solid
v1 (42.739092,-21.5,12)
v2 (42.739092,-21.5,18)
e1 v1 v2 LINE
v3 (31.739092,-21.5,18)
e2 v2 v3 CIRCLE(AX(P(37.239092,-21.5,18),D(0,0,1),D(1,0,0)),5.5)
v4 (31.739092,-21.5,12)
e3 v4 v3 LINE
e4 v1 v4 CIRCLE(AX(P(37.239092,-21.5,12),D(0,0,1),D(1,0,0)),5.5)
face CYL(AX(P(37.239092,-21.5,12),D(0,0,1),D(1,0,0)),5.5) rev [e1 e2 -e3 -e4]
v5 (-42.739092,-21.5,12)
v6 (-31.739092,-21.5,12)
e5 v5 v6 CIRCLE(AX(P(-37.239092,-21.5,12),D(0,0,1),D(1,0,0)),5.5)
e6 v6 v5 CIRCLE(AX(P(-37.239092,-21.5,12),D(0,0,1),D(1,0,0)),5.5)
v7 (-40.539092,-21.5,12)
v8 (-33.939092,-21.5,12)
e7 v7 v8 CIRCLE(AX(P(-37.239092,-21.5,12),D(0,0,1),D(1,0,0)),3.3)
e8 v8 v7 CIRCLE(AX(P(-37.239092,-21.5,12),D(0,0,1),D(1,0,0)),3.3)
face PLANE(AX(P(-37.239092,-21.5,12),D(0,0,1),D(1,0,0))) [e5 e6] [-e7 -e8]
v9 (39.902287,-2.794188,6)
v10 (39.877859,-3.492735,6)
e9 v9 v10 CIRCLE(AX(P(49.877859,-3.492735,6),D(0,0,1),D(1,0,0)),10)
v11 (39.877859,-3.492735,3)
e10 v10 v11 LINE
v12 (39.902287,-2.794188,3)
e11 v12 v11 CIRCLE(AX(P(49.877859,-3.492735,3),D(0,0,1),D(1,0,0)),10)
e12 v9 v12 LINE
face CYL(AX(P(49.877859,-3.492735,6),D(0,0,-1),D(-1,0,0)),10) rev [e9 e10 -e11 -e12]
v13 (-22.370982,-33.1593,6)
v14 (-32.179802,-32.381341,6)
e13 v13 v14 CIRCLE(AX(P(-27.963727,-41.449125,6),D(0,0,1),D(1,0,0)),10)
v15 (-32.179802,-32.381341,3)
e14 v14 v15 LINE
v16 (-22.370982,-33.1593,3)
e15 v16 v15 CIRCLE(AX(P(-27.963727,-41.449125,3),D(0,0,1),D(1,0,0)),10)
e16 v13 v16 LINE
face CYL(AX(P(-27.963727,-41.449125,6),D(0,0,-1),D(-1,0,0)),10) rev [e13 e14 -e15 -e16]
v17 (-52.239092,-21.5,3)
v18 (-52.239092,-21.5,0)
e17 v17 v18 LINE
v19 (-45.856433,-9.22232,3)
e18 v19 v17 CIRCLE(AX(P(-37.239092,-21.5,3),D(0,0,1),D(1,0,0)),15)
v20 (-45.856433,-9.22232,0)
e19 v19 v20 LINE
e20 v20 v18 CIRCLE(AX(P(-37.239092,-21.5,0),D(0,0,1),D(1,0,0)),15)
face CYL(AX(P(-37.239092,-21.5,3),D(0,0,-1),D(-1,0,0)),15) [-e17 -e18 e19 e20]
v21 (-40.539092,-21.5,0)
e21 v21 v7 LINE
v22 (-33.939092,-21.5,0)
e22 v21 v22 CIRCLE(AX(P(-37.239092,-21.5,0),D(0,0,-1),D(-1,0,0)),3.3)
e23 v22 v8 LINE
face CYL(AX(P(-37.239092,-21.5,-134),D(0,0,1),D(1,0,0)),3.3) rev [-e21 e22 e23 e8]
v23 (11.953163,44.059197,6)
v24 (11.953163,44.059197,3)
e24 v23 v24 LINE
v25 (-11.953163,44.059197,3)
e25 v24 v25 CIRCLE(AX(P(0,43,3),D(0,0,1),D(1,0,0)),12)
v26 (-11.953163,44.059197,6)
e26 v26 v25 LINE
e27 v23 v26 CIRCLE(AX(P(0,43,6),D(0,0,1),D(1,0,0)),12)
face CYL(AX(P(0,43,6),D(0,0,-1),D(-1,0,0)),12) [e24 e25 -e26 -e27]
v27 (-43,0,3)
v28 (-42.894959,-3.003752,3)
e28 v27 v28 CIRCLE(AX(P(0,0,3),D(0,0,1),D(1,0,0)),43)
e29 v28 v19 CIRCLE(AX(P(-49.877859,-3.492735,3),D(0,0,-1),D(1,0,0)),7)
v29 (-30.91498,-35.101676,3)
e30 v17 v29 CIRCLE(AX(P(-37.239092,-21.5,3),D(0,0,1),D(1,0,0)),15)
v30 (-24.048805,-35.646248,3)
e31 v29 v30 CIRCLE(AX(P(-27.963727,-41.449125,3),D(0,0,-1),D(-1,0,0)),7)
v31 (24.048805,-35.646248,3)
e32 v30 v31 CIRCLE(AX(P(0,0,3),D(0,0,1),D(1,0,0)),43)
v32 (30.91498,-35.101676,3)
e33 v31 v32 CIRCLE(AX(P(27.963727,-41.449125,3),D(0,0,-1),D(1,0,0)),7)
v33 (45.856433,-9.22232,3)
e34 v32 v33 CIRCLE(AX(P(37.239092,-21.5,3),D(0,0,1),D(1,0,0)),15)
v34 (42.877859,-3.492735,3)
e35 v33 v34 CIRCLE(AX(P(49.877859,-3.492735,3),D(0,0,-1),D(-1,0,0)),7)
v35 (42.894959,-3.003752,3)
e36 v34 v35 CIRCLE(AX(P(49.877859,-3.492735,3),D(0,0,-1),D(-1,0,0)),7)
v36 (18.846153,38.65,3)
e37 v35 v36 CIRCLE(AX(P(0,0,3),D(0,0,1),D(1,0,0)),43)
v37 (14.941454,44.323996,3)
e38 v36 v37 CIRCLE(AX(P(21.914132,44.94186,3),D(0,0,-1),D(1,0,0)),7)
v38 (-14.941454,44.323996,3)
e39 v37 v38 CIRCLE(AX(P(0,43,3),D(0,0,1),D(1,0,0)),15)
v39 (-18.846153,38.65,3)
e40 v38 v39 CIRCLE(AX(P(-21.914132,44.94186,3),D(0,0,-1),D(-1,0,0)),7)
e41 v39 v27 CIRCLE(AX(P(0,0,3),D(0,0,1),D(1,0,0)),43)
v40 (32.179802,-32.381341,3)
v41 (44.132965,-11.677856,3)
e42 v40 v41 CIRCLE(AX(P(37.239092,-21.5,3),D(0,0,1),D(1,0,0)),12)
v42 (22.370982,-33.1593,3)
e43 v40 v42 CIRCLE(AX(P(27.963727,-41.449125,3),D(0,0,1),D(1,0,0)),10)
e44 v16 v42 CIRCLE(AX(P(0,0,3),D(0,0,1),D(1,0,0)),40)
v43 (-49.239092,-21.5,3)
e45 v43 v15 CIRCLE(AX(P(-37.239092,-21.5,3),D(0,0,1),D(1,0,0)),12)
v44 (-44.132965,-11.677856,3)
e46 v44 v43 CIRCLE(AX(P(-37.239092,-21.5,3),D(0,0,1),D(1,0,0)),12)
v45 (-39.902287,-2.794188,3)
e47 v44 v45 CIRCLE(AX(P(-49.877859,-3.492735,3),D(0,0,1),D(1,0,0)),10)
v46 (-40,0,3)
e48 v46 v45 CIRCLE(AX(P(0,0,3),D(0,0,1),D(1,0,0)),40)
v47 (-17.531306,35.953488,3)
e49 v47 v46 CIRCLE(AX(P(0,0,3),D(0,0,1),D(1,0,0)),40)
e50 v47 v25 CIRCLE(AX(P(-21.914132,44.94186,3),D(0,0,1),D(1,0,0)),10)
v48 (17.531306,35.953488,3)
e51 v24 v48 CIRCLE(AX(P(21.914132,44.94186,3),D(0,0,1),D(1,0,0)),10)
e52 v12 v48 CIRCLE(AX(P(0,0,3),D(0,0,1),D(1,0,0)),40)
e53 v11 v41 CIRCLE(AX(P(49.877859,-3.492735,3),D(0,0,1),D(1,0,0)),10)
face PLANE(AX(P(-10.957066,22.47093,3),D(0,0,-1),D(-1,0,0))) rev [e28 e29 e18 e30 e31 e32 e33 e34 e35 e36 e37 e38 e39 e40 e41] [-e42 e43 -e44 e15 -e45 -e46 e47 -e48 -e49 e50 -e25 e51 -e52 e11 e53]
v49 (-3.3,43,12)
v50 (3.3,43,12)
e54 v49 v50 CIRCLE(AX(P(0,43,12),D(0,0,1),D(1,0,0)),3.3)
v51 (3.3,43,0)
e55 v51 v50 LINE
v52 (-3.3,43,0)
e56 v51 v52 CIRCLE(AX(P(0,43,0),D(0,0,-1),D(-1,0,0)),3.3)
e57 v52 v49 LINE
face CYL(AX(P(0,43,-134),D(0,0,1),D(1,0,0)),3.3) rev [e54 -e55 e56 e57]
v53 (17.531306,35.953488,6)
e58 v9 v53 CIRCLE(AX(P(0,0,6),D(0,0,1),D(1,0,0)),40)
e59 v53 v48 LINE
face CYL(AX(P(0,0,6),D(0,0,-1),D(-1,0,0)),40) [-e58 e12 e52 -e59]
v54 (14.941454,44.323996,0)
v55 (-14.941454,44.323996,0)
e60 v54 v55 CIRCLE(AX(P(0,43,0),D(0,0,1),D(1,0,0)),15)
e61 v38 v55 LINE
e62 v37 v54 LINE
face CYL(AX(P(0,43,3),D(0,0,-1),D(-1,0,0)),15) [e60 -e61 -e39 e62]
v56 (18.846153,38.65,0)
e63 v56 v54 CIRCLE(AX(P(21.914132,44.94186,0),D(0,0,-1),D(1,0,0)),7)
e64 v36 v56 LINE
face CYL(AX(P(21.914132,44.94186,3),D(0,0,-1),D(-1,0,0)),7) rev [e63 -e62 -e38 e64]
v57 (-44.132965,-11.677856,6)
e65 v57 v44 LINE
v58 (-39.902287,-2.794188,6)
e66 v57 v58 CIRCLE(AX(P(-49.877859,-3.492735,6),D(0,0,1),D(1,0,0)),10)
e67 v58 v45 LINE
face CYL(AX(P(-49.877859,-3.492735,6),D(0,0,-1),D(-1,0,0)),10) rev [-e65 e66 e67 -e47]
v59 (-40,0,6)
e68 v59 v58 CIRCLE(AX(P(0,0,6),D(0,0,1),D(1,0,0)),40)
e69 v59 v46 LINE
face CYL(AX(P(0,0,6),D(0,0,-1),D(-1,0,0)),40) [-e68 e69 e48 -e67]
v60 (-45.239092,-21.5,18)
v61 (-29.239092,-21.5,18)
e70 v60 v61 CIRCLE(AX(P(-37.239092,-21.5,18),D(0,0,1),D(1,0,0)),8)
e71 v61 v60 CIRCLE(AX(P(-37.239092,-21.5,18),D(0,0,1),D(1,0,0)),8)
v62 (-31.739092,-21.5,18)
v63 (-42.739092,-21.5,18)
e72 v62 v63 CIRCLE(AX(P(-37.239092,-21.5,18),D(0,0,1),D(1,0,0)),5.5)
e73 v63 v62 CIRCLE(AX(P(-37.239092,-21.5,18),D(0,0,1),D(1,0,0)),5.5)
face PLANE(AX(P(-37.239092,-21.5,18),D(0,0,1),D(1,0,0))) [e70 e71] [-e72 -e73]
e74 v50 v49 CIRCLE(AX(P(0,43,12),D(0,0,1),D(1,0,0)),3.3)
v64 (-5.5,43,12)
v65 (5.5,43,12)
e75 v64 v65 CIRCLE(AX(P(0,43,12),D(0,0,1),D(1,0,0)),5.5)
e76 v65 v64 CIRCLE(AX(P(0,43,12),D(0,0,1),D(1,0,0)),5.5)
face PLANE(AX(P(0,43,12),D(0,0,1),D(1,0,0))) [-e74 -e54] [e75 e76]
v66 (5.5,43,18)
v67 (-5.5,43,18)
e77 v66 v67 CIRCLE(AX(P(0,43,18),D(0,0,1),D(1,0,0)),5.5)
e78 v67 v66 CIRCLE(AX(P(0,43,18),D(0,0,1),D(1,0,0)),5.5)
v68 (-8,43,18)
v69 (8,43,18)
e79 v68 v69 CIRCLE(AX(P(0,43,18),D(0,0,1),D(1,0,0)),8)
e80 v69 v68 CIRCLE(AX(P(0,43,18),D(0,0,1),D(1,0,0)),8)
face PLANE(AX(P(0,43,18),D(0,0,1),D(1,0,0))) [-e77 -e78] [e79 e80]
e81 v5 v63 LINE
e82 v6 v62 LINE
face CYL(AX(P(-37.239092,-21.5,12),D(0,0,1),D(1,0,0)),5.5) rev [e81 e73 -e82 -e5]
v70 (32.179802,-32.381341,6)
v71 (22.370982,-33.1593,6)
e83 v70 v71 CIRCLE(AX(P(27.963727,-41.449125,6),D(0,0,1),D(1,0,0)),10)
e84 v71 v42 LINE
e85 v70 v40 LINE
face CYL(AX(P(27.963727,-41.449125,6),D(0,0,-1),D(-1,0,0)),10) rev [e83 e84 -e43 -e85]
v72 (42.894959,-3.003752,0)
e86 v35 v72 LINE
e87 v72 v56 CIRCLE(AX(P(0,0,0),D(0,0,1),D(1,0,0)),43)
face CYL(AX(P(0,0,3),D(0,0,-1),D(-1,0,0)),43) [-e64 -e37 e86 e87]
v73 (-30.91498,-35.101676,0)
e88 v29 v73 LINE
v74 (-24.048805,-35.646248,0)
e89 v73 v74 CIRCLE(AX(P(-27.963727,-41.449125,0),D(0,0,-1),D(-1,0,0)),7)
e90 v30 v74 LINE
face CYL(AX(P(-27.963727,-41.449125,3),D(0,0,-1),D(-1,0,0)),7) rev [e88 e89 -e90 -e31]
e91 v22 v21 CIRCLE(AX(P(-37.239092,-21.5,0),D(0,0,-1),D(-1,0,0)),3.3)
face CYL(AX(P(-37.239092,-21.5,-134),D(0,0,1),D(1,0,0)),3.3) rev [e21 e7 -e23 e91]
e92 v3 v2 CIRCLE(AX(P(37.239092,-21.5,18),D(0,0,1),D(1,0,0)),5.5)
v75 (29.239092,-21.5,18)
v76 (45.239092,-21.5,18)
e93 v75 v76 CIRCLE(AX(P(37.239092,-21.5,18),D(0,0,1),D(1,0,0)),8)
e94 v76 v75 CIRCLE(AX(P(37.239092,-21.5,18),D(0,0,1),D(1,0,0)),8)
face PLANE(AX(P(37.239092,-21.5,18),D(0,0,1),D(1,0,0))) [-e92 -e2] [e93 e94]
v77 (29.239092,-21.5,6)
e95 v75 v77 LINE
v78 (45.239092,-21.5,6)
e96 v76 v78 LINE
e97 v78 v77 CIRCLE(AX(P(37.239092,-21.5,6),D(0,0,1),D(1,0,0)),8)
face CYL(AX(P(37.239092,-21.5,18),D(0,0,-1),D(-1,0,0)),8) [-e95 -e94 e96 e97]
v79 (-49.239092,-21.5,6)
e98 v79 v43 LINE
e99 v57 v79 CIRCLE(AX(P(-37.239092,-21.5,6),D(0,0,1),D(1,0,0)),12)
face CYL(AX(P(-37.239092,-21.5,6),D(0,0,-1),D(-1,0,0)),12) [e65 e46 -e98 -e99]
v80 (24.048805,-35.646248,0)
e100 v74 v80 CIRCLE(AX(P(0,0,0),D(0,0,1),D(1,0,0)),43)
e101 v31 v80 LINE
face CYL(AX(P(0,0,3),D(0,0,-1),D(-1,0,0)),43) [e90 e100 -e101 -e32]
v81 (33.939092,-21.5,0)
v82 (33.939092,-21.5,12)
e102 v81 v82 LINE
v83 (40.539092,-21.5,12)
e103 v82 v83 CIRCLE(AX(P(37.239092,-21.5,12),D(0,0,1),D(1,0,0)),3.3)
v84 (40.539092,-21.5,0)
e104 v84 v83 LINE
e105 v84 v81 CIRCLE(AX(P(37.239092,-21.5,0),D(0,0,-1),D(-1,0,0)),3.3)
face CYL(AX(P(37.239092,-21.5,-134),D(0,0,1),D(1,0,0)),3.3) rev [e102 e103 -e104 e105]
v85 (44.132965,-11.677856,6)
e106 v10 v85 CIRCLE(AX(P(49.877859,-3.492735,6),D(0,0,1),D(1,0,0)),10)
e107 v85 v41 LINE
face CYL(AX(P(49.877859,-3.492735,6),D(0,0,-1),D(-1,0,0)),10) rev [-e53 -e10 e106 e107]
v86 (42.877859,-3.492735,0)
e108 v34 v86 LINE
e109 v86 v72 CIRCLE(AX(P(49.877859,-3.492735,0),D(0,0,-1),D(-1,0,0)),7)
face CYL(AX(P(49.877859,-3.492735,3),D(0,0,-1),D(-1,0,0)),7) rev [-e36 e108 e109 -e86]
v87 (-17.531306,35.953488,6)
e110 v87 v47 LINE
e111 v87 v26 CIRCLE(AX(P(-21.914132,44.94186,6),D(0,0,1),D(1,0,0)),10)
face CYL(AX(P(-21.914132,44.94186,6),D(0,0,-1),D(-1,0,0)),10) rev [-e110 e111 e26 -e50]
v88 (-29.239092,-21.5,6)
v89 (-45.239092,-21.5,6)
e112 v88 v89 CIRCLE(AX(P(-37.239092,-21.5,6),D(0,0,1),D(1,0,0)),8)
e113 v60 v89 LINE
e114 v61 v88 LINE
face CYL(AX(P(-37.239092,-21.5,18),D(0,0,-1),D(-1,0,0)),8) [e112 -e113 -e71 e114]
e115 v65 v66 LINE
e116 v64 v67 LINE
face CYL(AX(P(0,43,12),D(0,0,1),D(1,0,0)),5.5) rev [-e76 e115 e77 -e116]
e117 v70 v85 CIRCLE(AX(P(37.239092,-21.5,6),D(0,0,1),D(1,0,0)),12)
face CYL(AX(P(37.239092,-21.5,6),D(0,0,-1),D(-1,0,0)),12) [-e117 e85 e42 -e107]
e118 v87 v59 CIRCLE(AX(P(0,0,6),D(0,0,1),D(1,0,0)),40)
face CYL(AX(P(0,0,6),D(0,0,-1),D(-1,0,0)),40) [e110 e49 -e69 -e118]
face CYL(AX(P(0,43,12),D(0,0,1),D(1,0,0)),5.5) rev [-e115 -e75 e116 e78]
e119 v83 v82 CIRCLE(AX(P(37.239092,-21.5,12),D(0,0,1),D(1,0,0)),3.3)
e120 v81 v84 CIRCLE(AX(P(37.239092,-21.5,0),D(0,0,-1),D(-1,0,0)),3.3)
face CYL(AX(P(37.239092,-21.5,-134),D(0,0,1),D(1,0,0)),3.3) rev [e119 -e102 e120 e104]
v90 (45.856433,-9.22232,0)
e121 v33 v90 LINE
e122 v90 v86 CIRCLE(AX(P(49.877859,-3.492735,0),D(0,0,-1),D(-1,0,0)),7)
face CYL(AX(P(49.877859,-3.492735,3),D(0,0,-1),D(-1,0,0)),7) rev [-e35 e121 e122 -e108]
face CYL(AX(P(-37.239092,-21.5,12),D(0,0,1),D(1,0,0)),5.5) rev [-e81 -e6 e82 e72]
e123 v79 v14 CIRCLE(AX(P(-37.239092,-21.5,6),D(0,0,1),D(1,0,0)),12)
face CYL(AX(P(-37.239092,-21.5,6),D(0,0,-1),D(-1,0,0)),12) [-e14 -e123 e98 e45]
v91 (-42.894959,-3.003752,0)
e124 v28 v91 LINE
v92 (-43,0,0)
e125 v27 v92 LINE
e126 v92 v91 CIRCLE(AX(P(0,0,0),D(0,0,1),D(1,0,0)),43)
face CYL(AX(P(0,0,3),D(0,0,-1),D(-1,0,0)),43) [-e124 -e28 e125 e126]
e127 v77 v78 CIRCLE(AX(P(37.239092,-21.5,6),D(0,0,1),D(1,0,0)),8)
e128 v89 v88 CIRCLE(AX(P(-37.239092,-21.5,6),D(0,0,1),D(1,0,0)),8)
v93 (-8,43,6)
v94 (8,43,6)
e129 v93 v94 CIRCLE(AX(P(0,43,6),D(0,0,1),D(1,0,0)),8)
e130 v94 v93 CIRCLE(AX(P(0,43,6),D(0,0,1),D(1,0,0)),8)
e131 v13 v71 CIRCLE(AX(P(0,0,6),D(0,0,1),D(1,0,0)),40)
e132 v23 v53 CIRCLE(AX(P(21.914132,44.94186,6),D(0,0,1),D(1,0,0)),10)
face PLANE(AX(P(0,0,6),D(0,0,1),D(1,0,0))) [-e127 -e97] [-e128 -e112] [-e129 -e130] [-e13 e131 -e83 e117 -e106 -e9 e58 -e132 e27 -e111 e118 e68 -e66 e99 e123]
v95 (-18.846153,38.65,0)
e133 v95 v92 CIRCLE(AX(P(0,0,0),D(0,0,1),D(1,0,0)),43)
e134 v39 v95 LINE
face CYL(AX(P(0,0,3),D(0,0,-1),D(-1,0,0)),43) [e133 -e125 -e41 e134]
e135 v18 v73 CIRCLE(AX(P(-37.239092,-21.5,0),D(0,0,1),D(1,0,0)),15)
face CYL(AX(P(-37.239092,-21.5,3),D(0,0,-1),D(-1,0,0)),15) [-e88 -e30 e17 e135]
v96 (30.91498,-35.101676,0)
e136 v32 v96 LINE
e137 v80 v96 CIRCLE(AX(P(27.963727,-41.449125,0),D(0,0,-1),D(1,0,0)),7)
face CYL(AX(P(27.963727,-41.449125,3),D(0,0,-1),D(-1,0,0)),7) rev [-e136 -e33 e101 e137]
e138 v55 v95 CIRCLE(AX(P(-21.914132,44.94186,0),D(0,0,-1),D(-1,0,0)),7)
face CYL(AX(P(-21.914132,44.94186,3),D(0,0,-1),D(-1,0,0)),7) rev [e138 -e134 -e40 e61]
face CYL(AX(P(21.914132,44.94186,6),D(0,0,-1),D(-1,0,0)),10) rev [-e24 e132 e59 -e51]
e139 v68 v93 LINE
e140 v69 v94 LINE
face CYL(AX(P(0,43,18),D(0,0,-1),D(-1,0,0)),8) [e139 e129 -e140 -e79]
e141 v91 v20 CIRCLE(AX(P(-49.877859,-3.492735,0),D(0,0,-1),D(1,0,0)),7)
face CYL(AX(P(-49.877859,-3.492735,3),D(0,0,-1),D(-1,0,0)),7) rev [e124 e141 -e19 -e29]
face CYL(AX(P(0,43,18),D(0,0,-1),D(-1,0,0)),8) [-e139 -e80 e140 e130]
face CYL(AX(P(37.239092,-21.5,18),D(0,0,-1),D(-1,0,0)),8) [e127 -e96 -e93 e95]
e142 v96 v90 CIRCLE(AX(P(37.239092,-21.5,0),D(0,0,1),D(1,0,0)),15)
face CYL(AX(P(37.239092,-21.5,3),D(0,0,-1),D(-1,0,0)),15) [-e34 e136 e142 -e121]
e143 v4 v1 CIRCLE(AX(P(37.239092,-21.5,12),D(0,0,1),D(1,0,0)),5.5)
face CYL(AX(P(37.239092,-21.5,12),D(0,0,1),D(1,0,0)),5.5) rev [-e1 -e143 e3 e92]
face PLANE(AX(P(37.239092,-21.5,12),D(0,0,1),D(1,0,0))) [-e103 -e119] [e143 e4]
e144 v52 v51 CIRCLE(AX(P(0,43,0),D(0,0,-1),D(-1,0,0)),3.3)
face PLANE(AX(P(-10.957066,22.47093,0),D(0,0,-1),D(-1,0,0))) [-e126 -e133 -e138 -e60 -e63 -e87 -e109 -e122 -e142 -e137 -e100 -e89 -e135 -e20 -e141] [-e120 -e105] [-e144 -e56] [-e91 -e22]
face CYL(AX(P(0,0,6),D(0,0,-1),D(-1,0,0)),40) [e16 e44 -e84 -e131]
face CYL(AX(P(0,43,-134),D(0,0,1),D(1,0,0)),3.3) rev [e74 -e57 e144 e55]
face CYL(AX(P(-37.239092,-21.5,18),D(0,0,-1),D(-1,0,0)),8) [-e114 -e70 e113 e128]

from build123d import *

# Parameters (mm, degrees)
BASE_PLATE_3MM_DEPTH              = 3
RAISED_STEP_3MM_DEPTH             = 3
BOSS_PROFILE_3X_16_R              = 8
BOSSES_3X_16X12_DEPTH             = 12
COUNTERBORE_PROFILE_3X_11_R       = 5.5
COUNTERBORES_3X_11X6_DEPTH        = 6
CLEARANCE_HOLE_PROFILE_3X_6_6_R   = 3.3
CLEARANCE_HOLES_3X_6_6_THRU_DEPTH = 146


with BuildPart() as part:
    # Base Plate Profile → Base Plate 3mm (new body)
    with BuildSketch(Plane.XY):
        with BuildLine():
            ThreePointArc((-18.846153454, 38.65), (-37.239092363, 21.5), (-42.894958583, -3.003752345))
            ThreePointArc((-42.894958583, -3.003752345), (-43.557934635, -6.502479184), (-45.856433127, -9.222319513))
            ThreePointArc((-45.856433127, -9.222319513), (-50.229473419, -29), (-30.914979544, -35.101676259))
            ThreePointArc((-30.914979544, -35.101676259), (-27.410279478, -34.471038339), (-24.048805129, -35.646247655))
            ThreePointArc((-24.048805129, -35.646247655), (0, -43), (24.048805129, -35.646247655))
            ThreePointArc((24.048805129, -35.646247655), (27.410279478, -34.471038339), (30.914979544, -35.101676259))
            ThreePointArc((30.914979544, -35.101676259), (50.22947342, -29), (45.856433127, -9.222319513))
            ThreePointArc((45.856433127, -9.222319513), (43.557934635, -6.502479184), (42.894958583, -3.003752345))
            ThreePointArc((42.894958583, -3.003752345), (37.239092363, 21.5), (18.846153454, 38.65))
            ThreePointArc((18.846153454, 38.65), (16.147655157, 40.973517522), (14.941453584, 44.323995772))
            ThreePointArc((14.941453584, 44.323995772), (0, 58), (-14.941453584, 44.323995772))
            ThreePointArc((-14.941453584, 44.323995772), (-16.147655157, 40.973517522), (-18.846153454, 38.65))
        make_face()
    extrude(amount=BASE_PLATE_3MM_DEPTH)

    # Raised Step Profile → Raised Step 3mm (add)
    with BuildSketch(Plane.XY.offset(3)):
        with BuildLine():
            ThreePointArc((-17.531305538, 35.953488372), (-13.676307972, 39.272799119), (-11.953162867, 44.059196617))
            ThreePointArc((-11.953162867, 44.059196617), (0, 55), (11.953162867, 44.059196617))
            ThreePointArc((11.953162867, 44.059196617), (13.676307972, 39.272799119), (17.531305538, 35.953488372))
            ThreePointArc((17.531305538, 35.953488372), (34.641016151, 20), (39.902287054, -2.794188228))
            ThreePointArc((39.902287054, -2.794188228), (40.8493957, -7.792369426), (44.132964974, -11.67785561))
            ThreePointArc((44.132964974, -11.67785561), (47.631397208, -27.5), (32.179802107, -32.381341007))
            ThreePointArc((32.179802107, -32.381341007), (27.173087728, -31.480429693), (22.370981516, -33.159300144))
            ThreePointArc((22.370981516, -33.159300144), (0, -40), (-22.370981516, -33.159300144))
            ThreePointArc((-22.370981516, -33.159300144), (-27.173087728, -31.480429693), (-32.179802107, -32.381341007))
            ThreePointArc((-32.179802107, -32.381341007), (-47.631397208, -27.5), (-44.132964974, -11.67785561))
            ThreePointArc((-44.132964974, -11.67785561), (-40.8493957, -7.792369426), (-39.902287054, -2.794188228))
            ThreePointArc((-39.902287054, -2.794188228), (-34.641016151, 20), (-17.531305538, 35.953488372))
        make_face()
    extrude(amount=RAISED_STEP_3MM_DEPTH)

    # Boss Profile 3xØ16 → Bosses 3xØ16x12 (add)
    with BuildSketch(Plane.XY.offset(6)):
        with Locations((0, 43)):
            Circle(BOSS_PROFILE_3X_16_R)
        with Locations((37.239092363, -21.5)):
            Circle(BOSS_PROFILE_3X_16_R)
        with Locations((-37.239092363, -21.5)):
            Circle(BOSS_PROFILE_3X_16_R)
    extrude(amount=BOSSES_3X_16X12_DEPTH)

    # Counterbore Profile 3xØ11 → Counterbores 3xØ11x6 (cut)
    with BuildSketch(Plane.XY.offset(18)):
        with Locations((0, 43)):
            Circle(COUNTERBORE_PROFILE_3X_11_R)
        with Locations((37.239092363, -21.5)):
            Circle(COUNTERBORE_PROFILE_3X_11_R)
        with Locations((-37.239092363, -21.5)):
            Circle(COUNTERBORE_PROFILE_3X_11_R)
    extrude(amount=-COUNTERBORES_3X_11X6_DEPTH, mode=Mode.SUBTRACT)

    # Clearance Hole Profile 3xØ6.6 → Clearance Holes 3xØ6.6 Thru (cut)
    with BuildSketch(Plane.XY.offset(12)):
        with Locations((0, 43)):
            Circle(CLEARANCE_HOLE_PROFILE_3X_6_6_R)
        with Locations((37.239092363, -21.5)):
            Circle(CLEARANCE_HOLE_PROFILE_3X_6_6_R)
        with Locations((-37.239092363, -21.5)):
            Circle(CLEARANCE_HOLE_PROFILE_3X_6_6_R)
    extrude(amount=-CLEARANCE_HOLES_3X_6_6_THRU_DEPTH, mode=Mode.SUBTRACT)


solid = part.part
